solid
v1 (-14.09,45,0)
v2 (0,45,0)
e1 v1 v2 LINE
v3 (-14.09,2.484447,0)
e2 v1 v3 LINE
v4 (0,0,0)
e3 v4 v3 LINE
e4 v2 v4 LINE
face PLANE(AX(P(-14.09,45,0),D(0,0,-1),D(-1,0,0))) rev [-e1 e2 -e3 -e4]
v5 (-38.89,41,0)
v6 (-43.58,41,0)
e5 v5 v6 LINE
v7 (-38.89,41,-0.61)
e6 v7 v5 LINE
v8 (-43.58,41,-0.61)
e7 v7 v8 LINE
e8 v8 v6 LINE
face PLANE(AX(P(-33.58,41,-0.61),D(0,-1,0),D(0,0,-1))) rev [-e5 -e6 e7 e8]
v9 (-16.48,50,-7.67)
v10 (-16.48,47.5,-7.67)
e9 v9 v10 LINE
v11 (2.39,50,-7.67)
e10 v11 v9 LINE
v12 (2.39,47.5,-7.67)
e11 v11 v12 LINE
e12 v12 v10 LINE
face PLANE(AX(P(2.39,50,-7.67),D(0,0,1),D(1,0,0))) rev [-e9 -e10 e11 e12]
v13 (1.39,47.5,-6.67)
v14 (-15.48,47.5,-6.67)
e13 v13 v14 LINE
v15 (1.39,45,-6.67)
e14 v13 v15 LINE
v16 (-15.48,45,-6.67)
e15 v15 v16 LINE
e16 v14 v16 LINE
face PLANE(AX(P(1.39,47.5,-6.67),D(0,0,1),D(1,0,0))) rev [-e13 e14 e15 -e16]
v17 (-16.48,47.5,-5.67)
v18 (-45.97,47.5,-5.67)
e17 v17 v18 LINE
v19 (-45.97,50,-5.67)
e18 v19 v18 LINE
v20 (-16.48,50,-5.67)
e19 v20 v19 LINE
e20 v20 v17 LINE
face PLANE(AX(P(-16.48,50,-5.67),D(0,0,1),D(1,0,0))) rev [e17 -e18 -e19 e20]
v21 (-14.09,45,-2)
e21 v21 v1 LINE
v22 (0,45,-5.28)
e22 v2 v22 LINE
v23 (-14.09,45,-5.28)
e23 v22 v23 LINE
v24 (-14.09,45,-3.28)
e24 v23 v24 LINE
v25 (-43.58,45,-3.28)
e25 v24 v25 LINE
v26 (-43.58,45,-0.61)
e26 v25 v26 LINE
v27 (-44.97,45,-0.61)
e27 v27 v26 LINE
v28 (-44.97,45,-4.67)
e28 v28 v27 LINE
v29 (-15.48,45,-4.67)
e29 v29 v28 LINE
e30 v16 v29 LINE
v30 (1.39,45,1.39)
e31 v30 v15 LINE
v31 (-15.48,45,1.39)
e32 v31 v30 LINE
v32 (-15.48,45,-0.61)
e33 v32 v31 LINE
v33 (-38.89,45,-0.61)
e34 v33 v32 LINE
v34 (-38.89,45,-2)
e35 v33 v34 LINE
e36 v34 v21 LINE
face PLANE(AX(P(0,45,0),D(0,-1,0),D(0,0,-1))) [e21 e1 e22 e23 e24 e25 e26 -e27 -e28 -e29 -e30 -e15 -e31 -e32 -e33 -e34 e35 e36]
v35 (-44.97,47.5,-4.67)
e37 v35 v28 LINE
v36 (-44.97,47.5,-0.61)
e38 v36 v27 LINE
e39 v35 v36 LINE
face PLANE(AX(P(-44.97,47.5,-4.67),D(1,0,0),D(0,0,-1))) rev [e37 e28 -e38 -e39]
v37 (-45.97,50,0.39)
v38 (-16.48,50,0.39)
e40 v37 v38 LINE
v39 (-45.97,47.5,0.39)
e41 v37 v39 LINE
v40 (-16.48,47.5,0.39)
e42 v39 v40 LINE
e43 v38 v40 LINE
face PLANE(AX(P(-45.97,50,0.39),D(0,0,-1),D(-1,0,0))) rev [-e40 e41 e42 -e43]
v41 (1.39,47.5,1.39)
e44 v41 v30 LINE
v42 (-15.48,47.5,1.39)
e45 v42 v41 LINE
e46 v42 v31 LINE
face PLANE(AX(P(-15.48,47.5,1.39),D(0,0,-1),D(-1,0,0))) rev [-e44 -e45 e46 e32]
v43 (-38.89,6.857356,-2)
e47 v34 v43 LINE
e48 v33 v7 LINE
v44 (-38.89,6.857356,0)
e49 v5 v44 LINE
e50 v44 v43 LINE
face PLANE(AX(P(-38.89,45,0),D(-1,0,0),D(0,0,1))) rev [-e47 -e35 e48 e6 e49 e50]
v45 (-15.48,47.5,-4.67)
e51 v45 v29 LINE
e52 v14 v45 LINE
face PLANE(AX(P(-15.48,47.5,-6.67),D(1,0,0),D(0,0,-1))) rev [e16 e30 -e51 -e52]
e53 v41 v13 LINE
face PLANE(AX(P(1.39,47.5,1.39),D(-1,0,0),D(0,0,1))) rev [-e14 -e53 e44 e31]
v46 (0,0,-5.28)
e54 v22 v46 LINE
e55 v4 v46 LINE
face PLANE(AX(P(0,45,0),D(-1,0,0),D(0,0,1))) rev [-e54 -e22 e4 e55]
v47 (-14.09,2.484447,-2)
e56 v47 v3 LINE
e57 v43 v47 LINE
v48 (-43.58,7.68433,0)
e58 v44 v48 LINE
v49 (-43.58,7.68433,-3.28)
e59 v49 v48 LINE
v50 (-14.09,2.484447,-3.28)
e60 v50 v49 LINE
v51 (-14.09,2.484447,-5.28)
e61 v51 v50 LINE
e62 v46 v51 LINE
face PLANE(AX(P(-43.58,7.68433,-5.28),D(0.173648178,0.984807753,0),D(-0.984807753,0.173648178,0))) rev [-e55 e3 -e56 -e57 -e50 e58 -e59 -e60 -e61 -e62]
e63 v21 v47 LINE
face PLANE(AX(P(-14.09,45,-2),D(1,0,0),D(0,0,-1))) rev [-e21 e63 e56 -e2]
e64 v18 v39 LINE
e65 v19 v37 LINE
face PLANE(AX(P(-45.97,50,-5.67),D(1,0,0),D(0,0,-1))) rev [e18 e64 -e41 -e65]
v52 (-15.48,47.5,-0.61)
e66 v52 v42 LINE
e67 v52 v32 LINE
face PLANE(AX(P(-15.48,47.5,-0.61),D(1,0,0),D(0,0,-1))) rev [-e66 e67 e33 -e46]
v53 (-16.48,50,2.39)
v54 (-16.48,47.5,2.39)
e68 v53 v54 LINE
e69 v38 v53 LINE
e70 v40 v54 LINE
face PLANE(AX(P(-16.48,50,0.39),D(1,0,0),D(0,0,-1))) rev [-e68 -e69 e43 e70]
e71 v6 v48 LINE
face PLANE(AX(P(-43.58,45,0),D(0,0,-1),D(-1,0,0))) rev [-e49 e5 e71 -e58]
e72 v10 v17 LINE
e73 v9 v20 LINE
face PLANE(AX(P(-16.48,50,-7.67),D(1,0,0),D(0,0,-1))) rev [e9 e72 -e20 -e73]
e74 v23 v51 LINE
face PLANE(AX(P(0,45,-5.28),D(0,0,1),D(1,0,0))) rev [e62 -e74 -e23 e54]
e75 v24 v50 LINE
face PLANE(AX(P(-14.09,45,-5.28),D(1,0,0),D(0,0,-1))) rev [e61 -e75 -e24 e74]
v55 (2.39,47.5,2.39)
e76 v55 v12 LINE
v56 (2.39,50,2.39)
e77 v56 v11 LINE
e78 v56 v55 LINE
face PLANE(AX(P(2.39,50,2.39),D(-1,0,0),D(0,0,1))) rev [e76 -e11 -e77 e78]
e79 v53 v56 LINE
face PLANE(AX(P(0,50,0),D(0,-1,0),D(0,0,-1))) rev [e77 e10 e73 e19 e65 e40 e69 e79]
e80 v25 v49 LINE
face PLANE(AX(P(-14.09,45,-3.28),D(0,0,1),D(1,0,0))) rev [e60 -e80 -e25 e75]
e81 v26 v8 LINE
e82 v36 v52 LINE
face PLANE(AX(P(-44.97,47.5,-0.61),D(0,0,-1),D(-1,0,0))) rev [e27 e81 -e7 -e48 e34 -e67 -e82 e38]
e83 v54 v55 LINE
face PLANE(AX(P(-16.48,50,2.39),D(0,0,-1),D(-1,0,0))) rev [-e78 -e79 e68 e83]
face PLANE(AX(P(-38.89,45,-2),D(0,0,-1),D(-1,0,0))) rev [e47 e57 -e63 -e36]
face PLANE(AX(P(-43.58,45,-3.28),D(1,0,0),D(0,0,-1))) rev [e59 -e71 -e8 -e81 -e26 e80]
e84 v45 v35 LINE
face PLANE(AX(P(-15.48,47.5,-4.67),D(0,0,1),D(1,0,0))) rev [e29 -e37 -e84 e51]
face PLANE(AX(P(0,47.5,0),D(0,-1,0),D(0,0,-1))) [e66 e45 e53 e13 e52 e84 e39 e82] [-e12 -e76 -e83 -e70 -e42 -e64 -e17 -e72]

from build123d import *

# Parameters (mm, degrees)
BOSS_EXTRUDE1_DEPTH = 45
CUT_EXTRUDE1_DEPTH  = 63.865688575
BOSS_EXTRUDE2_DEPTH = 2.5
BOSS_EXTRUDE3_DEPTH = 2.5
SKETCH5_W           = 0.61
SKETCH5_H           = 4
CUT_EXTRUDE2_DEPTH  = 10


with BuildPart() as part:
    # Sketch1 → Boss-Extrude1 (new body)
    with BuildSketch(Plane(origin=(0, 0, 0), x_dir=(1, 0, 0), z_dir=(0, 1, 0))):
        Polygon((-43.58, 0), (-38.89, 0), (-38.89, 2), (-14.09, 2), (-14.09, 0), (0, 0), (0, 5.28), (-14.09, 5.28), (-14.09, 3.28), (-43.58, 3.28), align=None)
    extrude(amount=BOSS_EXTRUDE1_DEPTH)

    # Sketch2 → Cut-Extrude1 (cut, through all)
    with BuildSketch(Plane.XY):
        Polygon((0, 0), (-43.58, 0), (-43.58, 7.684329819), align=None)
    extrude(amount=-CUT_EXTRUDE1_DEPTH, mode=Mode.SUBTRACT)

    # Sketch3 → Boss-Extrude2 (add)
    with BuildSketch(Plane(origin=(0, 45, 0), x_dir=(1, 0, 0), z_dir=(0, 1, 0))):
        Polygon((-44.97, 4.67), (-44.97, 0.61), (-15.48, 0.61), (-15.48, -1.39), (1.39, -1.39), (1.39, 6.67), (-15.48, 6.67), (-15.48, 4.67), align=None)
    extrude(amount=BOSS_EXTRUDE2_DEPTH)

    # Sketch4 → Boss-Extrude3 (add)
    with BuildSketch(Plane(origin=(0, 47.5, 0), x_dir=(1, 0, 0), z_dir=(0, 1, 0))):
        Polygon((-45.97, 5.67), (-45.97, -0.39), (-16.48, -0.39), (-16.48, -2.39), (2.39, -2.39), (2.39, 7.67), (-16.48, 7.67), (-16.48, 5.67), align=None)
    extrude(amount=BOSS_EXTRUDE3_DEPTH)

    # Sketch5 → Cut-Extrude2 (cut)
    with BuildSketch(Plane.ZY.offset(43.58)):
        with Locations((-0.305, 43)):
            Rectangle(SKETCH5_W, SKETCH5_H)
    extrude(amount=-CUT_EXTRUDE2_DEPTH, mode=Mode.SUBTRACT)


solid = part.part
